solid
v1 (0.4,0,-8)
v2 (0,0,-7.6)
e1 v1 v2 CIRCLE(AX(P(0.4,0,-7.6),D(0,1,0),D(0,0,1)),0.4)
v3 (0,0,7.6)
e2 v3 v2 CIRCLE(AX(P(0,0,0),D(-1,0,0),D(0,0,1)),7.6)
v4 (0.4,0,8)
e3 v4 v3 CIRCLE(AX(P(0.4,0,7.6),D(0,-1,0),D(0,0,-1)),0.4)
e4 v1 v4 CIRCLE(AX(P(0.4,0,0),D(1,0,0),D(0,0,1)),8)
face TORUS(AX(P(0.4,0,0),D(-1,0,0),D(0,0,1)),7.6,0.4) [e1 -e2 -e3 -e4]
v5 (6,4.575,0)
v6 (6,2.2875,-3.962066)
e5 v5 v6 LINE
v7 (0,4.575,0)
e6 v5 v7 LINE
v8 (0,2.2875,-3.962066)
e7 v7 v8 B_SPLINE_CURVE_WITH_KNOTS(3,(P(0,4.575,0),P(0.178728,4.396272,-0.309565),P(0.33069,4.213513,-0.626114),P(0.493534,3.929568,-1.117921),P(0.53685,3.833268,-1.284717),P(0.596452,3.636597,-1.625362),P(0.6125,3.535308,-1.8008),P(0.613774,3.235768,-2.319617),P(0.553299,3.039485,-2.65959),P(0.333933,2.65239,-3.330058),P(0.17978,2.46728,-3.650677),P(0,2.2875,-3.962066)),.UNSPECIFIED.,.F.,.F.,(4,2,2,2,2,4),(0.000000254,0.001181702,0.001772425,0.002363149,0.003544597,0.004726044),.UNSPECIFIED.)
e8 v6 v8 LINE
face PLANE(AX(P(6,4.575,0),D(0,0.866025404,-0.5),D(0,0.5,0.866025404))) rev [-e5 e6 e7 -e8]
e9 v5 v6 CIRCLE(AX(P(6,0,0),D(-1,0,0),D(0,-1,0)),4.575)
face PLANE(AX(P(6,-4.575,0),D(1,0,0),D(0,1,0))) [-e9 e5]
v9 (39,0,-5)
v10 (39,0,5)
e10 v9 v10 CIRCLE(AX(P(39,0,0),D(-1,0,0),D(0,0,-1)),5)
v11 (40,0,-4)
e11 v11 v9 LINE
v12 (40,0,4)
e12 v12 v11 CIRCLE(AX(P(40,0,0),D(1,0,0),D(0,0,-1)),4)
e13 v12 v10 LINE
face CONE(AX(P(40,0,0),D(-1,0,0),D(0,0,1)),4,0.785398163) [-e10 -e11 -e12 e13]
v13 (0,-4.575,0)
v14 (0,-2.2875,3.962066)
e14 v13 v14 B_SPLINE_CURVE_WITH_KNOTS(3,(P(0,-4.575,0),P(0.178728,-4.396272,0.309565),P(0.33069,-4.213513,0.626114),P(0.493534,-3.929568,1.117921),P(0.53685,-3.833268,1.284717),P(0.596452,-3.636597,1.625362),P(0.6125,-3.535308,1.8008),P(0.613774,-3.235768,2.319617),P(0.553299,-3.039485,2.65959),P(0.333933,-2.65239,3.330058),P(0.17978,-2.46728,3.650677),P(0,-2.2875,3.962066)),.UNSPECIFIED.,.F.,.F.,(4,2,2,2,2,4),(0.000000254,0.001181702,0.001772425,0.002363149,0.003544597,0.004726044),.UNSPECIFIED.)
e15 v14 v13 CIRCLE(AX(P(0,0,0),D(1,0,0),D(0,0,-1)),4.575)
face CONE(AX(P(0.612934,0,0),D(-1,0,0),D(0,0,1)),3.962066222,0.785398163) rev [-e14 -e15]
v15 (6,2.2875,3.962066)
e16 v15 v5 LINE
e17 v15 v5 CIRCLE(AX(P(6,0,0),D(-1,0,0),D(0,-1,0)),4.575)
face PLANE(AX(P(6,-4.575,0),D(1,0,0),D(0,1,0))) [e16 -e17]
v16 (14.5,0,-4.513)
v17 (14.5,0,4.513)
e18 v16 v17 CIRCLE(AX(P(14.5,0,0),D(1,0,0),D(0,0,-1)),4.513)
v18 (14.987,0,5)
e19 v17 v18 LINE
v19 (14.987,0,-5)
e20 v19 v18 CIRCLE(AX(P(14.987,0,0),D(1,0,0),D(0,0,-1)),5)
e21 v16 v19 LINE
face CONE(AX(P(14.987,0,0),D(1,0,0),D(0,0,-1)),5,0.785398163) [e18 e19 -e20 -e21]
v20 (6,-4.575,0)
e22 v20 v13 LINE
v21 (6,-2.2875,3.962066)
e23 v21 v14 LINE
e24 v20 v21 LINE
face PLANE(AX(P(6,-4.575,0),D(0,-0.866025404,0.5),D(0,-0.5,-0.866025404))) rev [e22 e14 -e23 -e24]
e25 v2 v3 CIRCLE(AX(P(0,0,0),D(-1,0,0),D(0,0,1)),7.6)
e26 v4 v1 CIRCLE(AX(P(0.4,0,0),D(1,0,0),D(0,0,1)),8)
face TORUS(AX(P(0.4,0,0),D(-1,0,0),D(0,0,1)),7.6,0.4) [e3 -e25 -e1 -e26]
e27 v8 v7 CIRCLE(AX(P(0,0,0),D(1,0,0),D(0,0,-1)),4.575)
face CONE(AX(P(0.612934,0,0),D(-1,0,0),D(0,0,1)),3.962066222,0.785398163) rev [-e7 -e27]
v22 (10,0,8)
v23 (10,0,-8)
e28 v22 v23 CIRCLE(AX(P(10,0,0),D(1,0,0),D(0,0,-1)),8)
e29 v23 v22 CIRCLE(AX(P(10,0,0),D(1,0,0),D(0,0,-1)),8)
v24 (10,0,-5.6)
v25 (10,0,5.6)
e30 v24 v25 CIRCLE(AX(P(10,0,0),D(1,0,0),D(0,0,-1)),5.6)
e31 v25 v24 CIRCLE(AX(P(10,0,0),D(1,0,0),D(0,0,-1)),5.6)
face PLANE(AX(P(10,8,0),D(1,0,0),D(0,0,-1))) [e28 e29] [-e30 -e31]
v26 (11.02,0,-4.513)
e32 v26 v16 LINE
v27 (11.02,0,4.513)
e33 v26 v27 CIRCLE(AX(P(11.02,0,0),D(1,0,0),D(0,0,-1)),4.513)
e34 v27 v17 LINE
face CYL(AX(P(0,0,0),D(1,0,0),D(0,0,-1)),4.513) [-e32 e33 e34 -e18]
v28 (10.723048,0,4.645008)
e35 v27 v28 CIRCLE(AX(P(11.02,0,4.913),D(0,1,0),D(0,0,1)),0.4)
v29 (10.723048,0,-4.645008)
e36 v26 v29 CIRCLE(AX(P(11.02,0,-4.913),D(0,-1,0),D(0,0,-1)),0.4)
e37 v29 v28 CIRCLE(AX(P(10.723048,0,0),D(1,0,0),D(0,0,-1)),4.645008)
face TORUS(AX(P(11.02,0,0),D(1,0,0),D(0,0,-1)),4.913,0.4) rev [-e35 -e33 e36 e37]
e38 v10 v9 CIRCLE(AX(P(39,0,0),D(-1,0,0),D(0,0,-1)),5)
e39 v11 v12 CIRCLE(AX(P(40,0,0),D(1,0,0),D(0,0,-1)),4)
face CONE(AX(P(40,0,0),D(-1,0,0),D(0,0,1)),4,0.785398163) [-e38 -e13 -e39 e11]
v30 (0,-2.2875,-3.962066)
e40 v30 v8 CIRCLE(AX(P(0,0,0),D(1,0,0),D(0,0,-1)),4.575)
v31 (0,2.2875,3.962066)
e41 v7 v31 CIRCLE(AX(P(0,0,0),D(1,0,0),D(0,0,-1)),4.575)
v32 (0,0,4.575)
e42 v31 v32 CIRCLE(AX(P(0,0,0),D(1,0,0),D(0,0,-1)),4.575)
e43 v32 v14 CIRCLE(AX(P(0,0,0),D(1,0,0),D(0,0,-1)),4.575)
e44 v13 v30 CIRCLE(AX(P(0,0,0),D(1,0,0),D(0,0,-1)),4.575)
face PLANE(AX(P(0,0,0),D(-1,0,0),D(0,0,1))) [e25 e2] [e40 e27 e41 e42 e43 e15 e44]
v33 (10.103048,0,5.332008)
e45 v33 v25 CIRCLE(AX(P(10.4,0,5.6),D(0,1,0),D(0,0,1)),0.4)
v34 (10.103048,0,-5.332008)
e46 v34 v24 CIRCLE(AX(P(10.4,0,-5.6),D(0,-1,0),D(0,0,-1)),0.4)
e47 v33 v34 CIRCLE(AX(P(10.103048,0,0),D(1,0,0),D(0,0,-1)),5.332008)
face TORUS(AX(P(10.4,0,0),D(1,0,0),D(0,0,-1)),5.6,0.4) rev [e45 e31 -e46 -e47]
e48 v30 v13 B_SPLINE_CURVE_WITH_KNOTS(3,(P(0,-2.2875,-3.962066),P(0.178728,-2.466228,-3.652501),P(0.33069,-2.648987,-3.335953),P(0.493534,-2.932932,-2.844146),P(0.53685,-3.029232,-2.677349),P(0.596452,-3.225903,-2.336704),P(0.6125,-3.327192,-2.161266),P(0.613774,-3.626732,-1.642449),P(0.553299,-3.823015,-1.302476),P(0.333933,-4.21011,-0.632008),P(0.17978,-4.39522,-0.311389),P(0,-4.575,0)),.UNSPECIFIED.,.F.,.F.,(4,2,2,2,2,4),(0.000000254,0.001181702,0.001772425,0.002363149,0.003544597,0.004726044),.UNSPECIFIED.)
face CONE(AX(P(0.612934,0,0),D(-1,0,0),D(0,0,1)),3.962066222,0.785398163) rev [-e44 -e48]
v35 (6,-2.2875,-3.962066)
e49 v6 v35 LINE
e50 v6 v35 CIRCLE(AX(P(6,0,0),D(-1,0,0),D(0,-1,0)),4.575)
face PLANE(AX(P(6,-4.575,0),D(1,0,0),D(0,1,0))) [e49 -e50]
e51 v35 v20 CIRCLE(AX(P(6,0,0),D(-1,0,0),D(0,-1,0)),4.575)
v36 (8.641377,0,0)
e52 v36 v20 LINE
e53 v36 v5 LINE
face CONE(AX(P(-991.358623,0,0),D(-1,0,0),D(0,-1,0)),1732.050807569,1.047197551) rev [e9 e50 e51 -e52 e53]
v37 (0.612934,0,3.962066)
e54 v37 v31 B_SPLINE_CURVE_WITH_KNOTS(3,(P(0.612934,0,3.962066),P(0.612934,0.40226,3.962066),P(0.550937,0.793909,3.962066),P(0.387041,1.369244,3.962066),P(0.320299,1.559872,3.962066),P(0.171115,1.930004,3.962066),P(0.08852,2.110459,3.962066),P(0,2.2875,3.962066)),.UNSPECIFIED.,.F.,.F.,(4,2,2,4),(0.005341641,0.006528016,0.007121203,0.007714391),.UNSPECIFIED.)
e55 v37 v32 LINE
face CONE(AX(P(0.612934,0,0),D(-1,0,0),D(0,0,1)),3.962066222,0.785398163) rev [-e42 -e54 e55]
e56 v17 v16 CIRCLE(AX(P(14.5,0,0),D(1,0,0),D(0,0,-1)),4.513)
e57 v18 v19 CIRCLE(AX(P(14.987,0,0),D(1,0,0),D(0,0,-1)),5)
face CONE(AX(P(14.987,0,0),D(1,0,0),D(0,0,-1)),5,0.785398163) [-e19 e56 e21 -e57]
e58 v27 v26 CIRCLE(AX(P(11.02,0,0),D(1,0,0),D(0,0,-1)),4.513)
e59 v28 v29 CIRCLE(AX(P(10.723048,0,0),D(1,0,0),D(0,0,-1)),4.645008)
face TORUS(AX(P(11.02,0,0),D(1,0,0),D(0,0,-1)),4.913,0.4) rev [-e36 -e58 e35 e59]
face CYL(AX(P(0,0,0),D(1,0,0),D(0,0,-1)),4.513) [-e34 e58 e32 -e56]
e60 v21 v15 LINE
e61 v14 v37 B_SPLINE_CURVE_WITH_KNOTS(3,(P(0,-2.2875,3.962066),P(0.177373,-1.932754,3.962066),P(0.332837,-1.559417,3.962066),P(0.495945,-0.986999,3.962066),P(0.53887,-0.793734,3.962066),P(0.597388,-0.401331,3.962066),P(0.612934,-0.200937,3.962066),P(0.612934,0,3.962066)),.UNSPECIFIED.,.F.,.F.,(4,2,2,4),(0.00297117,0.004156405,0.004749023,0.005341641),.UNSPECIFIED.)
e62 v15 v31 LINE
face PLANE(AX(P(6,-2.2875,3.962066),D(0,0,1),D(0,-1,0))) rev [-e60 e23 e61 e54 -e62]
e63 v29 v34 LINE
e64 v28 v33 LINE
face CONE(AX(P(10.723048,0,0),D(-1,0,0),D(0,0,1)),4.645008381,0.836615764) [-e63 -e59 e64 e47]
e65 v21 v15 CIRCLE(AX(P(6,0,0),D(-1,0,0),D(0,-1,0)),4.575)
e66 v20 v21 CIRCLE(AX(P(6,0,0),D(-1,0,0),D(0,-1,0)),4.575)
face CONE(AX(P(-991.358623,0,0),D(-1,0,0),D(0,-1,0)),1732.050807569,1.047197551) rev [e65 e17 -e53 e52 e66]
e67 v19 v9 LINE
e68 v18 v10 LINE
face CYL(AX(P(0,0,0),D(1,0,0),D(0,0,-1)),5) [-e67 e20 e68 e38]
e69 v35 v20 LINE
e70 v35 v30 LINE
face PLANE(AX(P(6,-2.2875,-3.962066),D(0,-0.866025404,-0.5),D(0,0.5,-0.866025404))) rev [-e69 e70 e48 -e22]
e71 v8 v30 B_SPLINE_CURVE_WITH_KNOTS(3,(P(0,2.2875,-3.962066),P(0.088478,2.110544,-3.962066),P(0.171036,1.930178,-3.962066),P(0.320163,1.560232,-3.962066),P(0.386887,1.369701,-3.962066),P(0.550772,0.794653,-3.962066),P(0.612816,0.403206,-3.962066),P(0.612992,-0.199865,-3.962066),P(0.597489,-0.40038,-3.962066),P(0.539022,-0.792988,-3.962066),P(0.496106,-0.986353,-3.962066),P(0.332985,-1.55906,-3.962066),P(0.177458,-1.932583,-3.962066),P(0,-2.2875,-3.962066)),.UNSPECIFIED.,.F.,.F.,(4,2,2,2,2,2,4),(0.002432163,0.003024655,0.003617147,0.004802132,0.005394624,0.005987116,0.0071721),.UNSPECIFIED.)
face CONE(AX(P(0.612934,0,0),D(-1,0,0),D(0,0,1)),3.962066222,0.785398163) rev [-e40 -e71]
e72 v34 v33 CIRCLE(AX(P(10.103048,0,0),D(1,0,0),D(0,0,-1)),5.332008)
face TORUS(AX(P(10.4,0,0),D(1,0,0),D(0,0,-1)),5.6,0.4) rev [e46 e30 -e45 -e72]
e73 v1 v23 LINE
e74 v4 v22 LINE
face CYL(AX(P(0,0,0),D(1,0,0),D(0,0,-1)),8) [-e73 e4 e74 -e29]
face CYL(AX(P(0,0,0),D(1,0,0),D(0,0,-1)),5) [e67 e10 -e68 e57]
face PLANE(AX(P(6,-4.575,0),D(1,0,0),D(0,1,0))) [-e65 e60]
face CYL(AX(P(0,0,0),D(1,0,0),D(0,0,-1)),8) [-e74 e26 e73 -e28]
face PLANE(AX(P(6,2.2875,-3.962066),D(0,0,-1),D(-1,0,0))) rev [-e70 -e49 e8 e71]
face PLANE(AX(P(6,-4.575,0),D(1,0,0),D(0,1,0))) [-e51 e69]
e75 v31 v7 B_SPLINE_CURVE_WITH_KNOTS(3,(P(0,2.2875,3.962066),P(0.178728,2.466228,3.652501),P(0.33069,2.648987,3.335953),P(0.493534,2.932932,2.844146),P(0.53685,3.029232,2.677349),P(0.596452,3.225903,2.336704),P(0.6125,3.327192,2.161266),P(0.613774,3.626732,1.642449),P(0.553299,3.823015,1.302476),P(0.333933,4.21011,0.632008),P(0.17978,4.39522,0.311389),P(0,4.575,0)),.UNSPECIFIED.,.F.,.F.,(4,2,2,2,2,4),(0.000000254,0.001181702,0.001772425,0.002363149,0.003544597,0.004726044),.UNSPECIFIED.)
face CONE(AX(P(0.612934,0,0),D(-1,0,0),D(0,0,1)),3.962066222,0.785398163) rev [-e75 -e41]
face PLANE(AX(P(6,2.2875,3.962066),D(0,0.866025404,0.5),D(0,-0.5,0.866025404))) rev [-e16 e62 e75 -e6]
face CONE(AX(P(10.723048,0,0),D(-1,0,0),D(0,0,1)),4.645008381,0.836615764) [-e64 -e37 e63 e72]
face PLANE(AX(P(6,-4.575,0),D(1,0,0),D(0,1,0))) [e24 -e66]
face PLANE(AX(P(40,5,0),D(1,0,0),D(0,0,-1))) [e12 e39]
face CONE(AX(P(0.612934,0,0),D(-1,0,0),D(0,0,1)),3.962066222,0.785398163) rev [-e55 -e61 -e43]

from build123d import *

# Parameters (mm, degrees)
CUT_EXTRUDE1_DEPTH = 6
FILLET1_R          = 0.4
CHAMFER1_SIZE      = 1


with BuildPart() as part:
    # Sketch1 → Base-Revolve (revolve)
    with BuildSketch(Plane.XY, mode=Mode.PRIVATE) as base_revolve_sk:
        with BuildLine():
            Line((0, 0), (0, 8))
            Line((0, 8), (10, 8))
            Line((10, 8), (10, 5.6))
            ThreePointArc((10, 5.6), (10.026649761, 5.456439562), (10.103047997, 5.332008381))
            Line((10.103047997, 5.332008381), (10.723047997, 4.645008381))
            ThreePointArc((10.723047997, 4.645008381), (10.857514074, 4.547488955), (11.02, 4.513))
            Line((11.02, 4.513), (14.5, 4.513))
            Line((14.5, 4.513), (14.987, 5))
            Line((14.987, 5), (40, 5))
            Line((40, 5), (40, 0))
            Line((40, 0), (0, 0))
        make_face()
    revolve(base_revolve_sk.sketch.rotate(Axis((0, 0, 0), (-1, 0, 0)), 90), axis=Axis((0, 0, 0), (-1, 0, 0)))

    # Sketch2 → Cut-Extrude1 (cut)
    with BuildSketch(Plane.ZY):
        Polygon((3.962066222, -2.2875), (3.962066222, 2.2875), (0, 4.575), (-3.962066222, 2.2875), (-3.962066222, -2.2875), (0, -4.575), align=None)
    extrude(amount=-CUT_EXTRUDE1_DEPTH, mode=Mode.SUBTRACT)

    # Sketch13 → Cut-Revolve4 (revolve, cut)
    with BuildSketch(Plane.XY):
        Polygon((0, 4.575), (0.612933778, 3.962066222), (0, 3.962066222), align=None)
    revolve(axis=Axis((0, 0, 0), (-1, 0, 0)), mode=Mode.SUBTRACT)

    # Sketch16 → Cut-Revolve5 (revolve, cut)
    with BuildSketch(Plane.XY, mode=Mode.PRIVATE) as cut_revolve5_sk:
        Polygon((8.641377482, 0), (6, 4.575), (6, 0), align=None)
    revolve(cut_revolve5_sk.sketch.rotate(Axis((6, 0, 0), (1, 0, 0)), 180), axis=Axis((6, 0, 0), (1, 0, 0)), mode=Mode.SUBTRACT)

    # Fillet1
    fillet1_edges = [part.edges().sort_by_distance(p)[0] for p in [
        (0, 0, 8),
    ]]
    fillet(fillet1_edges, radius=FILLET1_R)

    # Chamfer1
    chamfer1_edges = [part.edges().sort_by_distance(p)[0] for p in [
        (40, 0, 5),
    ]]
    chamfer(chamfer1_edges, length=CHAMFER1_SIZE)


solid = part.part
